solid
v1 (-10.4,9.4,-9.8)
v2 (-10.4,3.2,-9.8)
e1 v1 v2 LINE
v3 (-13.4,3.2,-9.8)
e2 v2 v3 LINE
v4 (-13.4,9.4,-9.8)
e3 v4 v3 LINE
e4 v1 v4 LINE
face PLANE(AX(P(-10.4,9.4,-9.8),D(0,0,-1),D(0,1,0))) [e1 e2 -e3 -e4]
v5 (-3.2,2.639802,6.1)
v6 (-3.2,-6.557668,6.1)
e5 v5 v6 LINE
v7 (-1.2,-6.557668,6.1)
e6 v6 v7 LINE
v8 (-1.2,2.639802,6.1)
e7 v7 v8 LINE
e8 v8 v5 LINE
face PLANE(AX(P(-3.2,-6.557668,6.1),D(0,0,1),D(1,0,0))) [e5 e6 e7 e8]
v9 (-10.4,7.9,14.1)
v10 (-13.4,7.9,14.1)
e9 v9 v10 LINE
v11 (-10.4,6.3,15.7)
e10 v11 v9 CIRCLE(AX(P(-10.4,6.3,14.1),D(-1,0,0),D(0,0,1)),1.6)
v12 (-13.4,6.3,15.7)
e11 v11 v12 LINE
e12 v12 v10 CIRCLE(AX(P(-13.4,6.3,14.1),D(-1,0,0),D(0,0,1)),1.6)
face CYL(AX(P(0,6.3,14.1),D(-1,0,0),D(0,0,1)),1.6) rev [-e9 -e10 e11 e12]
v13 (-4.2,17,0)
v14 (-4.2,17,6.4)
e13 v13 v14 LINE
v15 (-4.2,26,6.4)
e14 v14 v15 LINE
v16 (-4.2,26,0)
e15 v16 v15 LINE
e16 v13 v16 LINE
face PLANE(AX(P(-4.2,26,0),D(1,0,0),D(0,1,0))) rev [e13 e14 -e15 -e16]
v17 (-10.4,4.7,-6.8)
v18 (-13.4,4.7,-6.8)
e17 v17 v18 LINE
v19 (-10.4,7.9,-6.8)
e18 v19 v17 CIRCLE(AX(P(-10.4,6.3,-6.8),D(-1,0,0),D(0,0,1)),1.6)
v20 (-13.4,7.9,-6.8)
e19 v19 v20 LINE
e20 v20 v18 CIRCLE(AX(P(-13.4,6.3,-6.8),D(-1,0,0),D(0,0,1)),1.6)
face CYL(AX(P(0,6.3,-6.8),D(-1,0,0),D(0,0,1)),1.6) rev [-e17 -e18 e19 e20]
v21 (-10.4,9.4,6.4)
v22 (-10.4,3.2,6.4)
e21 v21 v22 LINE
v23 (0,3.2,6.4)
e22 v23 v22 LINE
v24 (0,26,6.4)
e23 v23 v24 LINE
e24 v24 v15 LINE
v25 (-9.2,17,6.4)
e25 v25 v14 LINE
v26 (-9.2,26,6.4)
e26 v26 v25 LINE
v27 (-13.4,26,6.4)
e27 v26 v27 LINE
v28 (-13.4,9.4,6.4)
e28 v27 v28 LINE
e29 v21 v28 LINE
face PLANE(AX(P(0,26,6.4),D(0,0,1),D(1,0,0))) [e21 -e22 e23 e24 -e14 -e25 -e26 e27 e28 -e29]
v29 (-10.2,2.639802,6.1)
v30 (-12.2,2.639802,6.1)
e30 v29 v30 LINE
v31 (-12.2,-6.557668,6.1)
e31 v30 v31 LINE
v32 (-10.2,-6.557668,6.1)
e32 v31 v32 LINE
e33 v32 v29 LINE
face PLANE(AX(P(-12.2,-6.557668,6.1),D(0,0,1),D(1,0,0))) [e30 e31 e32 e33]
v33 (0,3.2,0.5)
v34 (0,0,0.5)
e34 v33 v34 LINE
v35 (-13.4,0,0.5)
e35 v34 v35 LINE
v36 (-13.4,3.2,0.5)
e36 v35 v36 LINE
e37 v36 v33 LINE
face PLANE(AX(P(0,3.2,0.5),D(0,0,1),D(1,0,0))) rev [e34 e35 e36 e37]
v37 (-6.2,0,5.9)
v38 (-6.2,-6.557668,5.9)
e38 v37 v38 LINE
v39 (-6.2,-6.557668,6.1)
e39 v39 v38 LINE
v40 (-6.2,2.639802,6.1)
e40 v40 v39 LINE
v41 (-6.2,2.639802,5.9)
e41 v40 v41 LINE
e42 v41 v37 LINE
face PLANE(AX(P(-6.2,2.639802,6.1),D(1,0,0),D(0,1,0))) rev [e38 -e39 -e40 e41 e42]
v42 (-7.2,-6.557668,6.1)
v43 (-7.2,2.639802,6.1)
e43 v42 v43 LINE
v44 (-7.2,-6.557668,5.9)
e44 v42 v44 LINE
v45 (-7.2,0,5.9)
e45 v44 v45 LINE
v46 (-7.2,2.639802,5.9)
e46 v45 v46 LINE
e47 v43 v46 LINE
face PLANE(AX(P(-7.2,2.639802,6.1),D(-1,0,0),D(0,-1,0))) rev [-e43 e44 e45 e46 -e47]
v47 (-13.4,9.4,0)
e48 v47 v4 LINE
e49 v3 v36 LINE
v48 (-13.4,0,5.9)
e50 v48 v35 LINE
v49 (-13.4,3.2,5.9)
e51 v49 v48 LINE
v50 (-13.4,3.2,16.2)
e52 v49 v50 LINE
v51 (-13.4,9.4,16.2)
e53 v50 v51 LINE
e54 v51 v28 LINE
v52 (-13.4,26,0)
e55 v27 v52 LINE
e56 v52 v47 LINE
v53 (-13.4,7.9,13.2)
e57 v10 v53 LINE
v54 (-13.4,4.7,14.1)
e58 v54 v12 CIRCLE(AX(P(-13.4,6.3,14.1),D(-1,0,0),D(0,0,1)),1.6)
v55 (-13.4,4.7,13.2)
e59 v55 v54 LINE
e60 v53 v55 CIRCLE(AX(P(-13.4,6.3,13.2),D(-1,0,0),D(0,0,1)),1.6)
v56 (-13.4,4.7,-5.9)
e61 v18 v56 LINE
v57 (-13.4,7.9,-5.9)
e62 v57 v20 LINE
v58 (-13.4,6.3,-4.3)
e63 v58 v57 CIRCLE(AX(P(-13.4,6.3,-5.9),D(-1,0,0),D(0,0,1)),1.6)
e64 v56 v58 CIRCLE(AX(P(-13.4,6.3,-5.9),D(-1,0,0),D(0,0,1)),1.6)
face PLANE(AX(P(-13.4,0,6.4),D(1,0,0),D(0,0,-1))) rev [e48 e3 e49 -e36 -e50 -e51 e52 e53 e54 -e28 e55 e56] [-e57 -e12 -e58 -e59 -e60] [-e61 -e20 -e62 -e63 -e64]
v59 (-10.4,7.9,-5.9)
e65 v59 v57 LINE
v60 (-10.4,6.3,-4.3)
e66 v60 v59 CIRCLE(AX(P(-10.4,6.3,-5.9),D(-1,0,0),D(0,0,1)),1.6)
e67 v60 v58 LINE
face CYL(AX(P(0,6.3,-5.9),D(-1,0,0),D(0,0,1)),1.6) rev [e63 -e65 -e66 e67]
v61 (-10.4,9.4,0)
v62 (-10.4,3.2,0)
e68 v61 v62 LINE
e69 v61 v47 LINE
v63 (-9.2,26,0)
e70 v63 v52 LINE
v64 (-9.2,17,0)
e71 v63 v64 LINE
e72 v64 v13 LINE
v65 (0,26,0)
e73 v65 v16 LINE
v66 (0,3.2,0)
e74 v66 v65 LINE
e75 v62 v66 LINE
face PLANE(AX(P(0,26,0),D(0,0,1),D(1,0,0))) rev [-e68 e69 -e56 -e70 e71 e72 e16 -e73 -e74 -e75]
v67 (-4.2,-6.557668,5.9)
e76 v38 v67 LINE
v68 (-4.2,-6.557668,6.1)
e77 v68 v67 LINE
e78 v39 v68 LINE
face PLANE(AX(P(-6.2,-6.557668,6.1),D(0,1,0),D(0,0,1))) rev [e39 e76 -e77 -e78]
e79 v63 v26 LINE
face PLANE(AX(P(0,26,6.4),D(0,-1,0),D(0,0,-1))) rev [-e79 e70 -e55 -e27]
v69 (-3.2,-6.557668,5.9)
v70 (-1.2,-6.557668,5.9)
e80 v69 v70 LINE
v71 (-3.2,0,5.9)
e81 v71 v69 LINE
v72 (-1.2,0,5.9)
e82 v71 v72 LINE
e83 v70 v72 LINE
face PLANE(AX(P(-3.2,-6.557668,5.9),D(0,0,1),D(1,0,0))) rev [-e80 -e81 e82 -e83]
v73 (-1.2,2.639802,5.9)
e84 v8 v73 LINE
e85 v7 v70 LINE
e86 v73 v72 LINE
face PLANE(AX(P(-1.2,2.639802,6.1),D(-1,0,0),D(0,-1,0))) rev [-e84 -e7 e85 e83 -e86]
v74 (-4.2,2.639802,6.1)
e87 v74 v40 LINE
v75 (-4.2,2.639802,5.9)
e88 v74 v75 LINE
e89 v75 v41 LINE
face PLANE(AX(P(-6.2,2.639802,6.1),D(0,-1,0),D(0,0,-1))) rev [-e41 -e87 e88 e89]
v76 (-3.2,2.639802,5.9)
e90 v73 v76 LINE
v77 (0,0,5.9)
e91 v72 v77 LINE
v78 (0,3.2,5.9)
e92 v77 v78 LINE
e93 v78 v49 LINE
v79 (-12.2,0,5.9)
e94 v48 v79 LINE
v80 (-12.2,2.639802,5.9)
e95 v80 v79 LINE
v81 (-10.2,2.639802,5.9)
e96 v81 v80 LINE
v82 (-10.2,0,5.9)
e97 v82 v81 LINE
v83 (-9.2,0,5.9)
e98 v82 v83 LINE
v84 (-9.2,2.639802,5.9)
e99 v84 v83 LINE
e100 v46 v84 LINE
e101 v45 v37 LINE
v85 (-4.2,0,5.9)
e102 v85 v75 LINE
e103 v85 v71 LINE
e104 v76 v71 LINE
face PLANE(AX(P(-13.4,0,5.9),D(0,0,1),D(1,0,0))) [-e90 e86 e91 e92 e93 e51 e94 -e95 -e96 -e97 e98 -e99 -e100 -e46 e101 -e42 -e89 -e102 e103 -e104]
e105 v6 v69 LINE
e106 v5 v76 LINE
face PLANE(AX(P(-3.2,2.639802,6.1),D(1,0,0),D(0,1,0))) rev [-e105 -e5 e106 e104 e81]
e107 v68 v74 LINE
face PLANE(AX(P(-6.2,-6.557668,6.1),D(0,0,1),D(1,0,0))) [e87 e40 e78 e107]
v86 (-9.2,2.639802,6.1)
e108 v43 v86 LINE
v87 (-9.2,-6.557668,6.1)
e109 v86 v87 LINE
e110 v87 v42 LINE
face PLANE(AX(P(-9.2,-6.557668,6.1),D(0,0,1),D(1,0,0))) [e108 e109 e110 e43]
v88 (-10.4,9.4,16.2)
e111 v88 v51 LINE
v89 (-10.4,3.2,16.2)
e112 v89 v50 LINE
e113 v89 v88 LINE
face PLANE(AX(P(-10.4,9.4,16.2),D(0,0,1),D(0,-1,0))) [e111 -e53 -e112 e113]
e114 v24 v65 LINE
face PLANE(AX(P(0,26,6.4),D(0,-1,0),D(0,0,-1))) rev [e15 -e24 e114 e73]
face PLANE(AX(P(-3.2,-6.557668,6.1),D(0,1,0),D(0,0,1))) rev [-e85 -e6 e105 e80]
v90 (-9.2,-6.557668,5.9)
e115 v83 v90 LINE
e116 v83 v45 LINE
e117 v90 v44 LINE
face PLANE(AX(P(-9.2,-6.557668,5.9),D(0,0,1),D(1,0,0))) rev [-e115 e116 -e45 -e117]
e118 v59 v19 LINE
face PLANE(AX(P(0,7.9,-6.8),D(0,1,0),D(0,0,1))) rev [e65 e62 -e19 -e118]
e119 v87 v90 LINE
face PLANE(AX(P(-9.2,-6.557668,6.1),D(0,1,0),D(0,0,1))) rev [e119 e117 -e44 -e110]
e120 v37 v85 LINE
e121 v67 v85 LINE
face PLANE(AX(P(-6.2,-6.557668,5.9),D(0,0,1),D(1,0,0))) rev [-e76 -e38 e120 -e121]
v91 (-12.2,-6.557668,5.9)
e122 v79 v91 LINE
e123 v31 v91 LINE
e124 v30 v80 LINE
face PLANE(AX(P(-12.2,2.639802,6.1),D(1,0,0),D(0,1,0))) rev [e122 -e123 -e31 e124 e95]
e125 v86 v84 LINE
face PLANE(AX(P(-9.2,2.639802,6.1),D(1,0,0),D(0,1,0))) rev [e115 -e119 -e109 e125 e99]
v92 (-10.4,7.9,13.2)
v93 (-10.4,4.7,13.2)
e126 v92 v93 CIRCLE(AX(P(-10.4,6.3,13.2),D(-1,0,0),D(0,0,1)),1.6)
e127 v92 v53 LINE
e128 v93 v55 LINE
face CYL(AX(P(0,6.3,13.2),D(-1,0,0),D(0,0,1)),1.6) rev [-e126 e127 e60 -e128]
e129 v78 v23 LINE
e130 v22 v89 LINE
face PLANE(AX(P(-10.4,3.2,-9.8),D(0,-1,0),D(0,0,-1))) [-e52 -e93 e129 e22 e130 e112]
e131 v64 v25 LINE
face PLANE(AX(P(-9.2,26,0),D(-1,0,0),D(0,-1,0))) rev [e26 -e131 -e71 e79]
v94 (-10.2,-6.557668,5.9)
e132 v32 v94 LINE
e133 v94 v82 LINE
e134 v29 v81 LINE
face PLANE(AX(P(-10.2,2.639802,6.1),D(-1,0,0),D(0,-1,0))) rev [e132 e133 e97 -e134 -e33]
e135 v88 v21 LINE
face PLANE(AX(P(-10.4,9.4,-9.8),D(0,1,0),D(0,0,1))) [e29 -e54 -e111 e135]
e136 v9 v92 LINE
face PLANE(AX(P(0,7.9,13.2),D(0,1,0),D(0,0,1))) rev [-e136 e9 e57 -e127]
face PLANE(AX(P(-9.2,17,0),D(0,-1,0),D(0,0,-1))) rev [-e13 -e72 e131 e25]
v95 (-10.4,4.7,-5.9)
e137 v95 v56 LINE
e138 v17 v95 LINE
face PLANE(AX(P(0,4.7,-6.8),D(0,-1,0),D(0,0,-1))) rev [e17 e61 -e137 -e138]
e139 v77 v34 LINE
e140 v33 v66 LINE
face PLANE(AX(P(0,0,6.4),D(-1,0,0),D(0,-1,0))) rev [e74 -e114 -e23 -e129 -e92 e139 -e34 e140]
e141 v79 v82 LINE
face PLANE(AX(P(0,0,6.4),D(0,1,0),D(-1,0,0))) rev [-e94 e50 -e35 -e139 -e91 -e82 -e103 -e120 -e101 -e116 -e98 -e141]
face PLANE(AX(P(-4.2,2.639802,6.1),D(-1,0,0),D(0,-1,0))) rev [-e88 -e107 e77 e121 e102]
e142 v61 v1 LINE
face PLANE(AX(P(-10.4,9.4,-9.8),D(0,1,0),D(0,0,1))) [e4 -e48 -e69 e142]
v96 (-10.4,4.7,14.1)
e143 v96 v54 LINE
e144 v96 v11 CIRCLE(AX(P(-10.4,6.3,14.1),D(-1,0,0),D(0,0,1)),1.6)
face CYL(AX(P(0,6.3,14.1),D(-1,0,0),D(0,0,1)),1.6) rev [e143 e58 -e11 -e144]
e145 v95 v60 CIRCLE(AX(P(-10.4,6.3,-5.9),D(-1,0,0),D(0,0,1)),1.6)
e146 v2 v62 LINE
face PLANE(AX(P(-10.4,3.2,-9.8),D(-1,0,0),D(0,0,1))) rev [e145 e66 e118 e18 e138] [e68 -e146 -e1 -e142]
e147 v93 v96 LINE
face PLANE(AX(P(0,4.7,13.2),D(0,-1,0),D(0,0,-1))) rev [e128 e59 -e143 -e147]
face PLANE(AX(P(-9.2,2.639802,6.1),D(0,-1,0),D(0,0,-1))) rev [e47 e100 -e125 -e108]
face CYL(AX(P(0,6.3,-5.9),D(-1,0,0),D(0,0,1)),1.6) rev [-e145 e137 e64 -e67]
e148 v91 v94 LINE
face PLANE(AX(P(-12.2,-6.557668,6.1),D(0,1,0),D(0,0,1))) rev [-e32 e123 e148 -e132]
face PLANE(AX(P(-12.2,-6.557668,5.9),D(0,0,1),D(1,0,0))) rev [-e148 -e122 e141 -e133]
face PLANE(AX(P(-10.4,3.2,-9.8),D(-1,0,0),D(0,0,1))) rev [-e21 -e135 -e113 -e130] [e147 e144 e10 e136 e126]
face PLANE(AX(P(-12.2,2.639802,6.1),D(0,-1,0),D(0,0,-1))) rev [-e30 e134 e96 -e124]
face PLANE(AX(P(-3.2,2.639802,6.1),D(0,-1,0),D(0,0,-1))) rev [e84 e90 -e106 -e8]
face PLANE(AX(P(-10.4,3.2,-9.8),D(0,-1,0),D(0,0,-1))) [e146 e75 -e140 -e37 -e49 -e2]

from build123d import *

# Parameters (mm, degrees)
SKETCH1_W           = 13.4
SKETCH1_H           = 26
BOSS_EXTRUDE1_DEPTH = 6.4
SKETCH2_W           = 5
SKETCH2_H           = 9
CUT_EXTRUDE1_DEPTH  = 30.941943825
SKETCH3_W           = 26
SKETCH3_H           = 6.2
BOSS_EXTRUDE2_DEPTH = 3
CUT_EXTRUDE2_DEPTH  = 34.436506995
SKETCH5_W           = 13.4
SKETCH5_H           = 3.2
CUT_EXTRUDE3_DEPTH  = 0.5
SKETCH6_W           = 13.4
SKETCH6_H           = 3.2
CUT_EXTRUDE4_DEPTH  = 0.5
SKETCH7_W           = 2
SKETCH7_H           = 9.197470194
BOSS_EXTRUDE3_DEPTH = 0.2
LPATTERN1_COUNT     = 4
LPATTERN1_PITCH     = 3


with BuildPart() as part:
    # Sketch1 → Boss-Extrude1 (new body)
    with BuildSketch(Plane.XY):
        with Locations((-6.7, 13)):
            Rectangle(SKETCH1_W, SKETCH1_H)
    extrude(amount=BOSS_EXTRUDE1_DEPTH)

    # Sketch2 → Cut-Extrude1 (cut, through all)
    with BuildSketch(Plane.XY.offset(6.4)):
        with Locations((-6.7, 21.5)):
            Rectangle(SKETCH2_W, SKETCH2_H)
    extrude(amount=-CUT_EXTRUDE1_DEPTH, mode=Mode.SUBTRACT)

    # Sketch3 → Boss-Extrude2 (add)
    with BuildSketch(Plane.ZY.offset(13.4)):
        with Locations((3.2, 6.3)):
            Rectangle(SKETCH3_W, SKETCH3_H)
    extrude(amount=-BOSS_EXTRUDE2_DEPTH)

    # Sketch4 → Cut-Extrude2 (cut, through all)
    with BuildSketch(Plane.ZY.offset(13.4)):
        with BuildLine():
            Line((-6.8, 7.9), (-5.9, 7.9))
            ThreePointArc((-5.9, 7.9), (-4.3, 6.3), (-5.9, 4.7))
            Line((-5.9, 4.7), (-6.8, 4.7))
            ThreePointArc((-6.8, 4.7), (-8.4, 6.3), (-6.8, 7.9))
        make_face()
        with BuildLine():
            Line((13.2, 7.9), (14.1, 7.9))
            ThreePointArc((14.1, 7.9), (15.7, 6.3), (14.1, 4.7))
            Line((14.1, 4.7), (13.2, 4.7))
            ThreePointArc((13.2, 4.7), (11.6, 6.3), (13.2, 7.9))
        make_face()
    extrude(amount=-CUT_EXTRUDE2_DEPTH, mode=Mode.SUBTRACT)

    # Sketch5 → Cut-Extrude3 (cut)
    with BuildSketch(Plane.XY.offset(6.4)):
        with Locations((-6.7, 1.6)):
            Rectangle(SKETCH5_W, SKETCH5_H)
    extrude(amount=-CUT_EXTRUDE3_DEPTH, mode=Mode.SUBTRACT)

    # Sketch6 → Cut-Extrude4 (cut)
    with BuildSketch(Plane(origin=(0, 0, 0), x_dir=(-1, 0, 0), z_dir=(0, 0, -1))):
        with Locations((6.7, 1.6)):
            Rectangle(SKETCH6_W, SKETCH6_H)
    extrude(amount=-CUT_EXTRUDE4_DEPTH, mode=Mode.SUBTRACT)

    # Sketch7 → Boss-Extrude3 (add)
    with BuildSketch(Plane.XY.offset(5.9)):
        with Locations((-2.2, -1.958933194)):
            Rectangle(SKETCH7_W, SKETCH7_H)
    boss_extrude3 = extrude(amount=BOSS_EXTRUDE3_DEPTH)

    # LPattern1: Boss-Extrude3 ×4
    with Locations(*[(-i * LPATTERN1_PITCH, 0, 0) for i in range(1, LPATTERN1_COUNT)]):
        add(boss_extrude3)


solid = part.part
